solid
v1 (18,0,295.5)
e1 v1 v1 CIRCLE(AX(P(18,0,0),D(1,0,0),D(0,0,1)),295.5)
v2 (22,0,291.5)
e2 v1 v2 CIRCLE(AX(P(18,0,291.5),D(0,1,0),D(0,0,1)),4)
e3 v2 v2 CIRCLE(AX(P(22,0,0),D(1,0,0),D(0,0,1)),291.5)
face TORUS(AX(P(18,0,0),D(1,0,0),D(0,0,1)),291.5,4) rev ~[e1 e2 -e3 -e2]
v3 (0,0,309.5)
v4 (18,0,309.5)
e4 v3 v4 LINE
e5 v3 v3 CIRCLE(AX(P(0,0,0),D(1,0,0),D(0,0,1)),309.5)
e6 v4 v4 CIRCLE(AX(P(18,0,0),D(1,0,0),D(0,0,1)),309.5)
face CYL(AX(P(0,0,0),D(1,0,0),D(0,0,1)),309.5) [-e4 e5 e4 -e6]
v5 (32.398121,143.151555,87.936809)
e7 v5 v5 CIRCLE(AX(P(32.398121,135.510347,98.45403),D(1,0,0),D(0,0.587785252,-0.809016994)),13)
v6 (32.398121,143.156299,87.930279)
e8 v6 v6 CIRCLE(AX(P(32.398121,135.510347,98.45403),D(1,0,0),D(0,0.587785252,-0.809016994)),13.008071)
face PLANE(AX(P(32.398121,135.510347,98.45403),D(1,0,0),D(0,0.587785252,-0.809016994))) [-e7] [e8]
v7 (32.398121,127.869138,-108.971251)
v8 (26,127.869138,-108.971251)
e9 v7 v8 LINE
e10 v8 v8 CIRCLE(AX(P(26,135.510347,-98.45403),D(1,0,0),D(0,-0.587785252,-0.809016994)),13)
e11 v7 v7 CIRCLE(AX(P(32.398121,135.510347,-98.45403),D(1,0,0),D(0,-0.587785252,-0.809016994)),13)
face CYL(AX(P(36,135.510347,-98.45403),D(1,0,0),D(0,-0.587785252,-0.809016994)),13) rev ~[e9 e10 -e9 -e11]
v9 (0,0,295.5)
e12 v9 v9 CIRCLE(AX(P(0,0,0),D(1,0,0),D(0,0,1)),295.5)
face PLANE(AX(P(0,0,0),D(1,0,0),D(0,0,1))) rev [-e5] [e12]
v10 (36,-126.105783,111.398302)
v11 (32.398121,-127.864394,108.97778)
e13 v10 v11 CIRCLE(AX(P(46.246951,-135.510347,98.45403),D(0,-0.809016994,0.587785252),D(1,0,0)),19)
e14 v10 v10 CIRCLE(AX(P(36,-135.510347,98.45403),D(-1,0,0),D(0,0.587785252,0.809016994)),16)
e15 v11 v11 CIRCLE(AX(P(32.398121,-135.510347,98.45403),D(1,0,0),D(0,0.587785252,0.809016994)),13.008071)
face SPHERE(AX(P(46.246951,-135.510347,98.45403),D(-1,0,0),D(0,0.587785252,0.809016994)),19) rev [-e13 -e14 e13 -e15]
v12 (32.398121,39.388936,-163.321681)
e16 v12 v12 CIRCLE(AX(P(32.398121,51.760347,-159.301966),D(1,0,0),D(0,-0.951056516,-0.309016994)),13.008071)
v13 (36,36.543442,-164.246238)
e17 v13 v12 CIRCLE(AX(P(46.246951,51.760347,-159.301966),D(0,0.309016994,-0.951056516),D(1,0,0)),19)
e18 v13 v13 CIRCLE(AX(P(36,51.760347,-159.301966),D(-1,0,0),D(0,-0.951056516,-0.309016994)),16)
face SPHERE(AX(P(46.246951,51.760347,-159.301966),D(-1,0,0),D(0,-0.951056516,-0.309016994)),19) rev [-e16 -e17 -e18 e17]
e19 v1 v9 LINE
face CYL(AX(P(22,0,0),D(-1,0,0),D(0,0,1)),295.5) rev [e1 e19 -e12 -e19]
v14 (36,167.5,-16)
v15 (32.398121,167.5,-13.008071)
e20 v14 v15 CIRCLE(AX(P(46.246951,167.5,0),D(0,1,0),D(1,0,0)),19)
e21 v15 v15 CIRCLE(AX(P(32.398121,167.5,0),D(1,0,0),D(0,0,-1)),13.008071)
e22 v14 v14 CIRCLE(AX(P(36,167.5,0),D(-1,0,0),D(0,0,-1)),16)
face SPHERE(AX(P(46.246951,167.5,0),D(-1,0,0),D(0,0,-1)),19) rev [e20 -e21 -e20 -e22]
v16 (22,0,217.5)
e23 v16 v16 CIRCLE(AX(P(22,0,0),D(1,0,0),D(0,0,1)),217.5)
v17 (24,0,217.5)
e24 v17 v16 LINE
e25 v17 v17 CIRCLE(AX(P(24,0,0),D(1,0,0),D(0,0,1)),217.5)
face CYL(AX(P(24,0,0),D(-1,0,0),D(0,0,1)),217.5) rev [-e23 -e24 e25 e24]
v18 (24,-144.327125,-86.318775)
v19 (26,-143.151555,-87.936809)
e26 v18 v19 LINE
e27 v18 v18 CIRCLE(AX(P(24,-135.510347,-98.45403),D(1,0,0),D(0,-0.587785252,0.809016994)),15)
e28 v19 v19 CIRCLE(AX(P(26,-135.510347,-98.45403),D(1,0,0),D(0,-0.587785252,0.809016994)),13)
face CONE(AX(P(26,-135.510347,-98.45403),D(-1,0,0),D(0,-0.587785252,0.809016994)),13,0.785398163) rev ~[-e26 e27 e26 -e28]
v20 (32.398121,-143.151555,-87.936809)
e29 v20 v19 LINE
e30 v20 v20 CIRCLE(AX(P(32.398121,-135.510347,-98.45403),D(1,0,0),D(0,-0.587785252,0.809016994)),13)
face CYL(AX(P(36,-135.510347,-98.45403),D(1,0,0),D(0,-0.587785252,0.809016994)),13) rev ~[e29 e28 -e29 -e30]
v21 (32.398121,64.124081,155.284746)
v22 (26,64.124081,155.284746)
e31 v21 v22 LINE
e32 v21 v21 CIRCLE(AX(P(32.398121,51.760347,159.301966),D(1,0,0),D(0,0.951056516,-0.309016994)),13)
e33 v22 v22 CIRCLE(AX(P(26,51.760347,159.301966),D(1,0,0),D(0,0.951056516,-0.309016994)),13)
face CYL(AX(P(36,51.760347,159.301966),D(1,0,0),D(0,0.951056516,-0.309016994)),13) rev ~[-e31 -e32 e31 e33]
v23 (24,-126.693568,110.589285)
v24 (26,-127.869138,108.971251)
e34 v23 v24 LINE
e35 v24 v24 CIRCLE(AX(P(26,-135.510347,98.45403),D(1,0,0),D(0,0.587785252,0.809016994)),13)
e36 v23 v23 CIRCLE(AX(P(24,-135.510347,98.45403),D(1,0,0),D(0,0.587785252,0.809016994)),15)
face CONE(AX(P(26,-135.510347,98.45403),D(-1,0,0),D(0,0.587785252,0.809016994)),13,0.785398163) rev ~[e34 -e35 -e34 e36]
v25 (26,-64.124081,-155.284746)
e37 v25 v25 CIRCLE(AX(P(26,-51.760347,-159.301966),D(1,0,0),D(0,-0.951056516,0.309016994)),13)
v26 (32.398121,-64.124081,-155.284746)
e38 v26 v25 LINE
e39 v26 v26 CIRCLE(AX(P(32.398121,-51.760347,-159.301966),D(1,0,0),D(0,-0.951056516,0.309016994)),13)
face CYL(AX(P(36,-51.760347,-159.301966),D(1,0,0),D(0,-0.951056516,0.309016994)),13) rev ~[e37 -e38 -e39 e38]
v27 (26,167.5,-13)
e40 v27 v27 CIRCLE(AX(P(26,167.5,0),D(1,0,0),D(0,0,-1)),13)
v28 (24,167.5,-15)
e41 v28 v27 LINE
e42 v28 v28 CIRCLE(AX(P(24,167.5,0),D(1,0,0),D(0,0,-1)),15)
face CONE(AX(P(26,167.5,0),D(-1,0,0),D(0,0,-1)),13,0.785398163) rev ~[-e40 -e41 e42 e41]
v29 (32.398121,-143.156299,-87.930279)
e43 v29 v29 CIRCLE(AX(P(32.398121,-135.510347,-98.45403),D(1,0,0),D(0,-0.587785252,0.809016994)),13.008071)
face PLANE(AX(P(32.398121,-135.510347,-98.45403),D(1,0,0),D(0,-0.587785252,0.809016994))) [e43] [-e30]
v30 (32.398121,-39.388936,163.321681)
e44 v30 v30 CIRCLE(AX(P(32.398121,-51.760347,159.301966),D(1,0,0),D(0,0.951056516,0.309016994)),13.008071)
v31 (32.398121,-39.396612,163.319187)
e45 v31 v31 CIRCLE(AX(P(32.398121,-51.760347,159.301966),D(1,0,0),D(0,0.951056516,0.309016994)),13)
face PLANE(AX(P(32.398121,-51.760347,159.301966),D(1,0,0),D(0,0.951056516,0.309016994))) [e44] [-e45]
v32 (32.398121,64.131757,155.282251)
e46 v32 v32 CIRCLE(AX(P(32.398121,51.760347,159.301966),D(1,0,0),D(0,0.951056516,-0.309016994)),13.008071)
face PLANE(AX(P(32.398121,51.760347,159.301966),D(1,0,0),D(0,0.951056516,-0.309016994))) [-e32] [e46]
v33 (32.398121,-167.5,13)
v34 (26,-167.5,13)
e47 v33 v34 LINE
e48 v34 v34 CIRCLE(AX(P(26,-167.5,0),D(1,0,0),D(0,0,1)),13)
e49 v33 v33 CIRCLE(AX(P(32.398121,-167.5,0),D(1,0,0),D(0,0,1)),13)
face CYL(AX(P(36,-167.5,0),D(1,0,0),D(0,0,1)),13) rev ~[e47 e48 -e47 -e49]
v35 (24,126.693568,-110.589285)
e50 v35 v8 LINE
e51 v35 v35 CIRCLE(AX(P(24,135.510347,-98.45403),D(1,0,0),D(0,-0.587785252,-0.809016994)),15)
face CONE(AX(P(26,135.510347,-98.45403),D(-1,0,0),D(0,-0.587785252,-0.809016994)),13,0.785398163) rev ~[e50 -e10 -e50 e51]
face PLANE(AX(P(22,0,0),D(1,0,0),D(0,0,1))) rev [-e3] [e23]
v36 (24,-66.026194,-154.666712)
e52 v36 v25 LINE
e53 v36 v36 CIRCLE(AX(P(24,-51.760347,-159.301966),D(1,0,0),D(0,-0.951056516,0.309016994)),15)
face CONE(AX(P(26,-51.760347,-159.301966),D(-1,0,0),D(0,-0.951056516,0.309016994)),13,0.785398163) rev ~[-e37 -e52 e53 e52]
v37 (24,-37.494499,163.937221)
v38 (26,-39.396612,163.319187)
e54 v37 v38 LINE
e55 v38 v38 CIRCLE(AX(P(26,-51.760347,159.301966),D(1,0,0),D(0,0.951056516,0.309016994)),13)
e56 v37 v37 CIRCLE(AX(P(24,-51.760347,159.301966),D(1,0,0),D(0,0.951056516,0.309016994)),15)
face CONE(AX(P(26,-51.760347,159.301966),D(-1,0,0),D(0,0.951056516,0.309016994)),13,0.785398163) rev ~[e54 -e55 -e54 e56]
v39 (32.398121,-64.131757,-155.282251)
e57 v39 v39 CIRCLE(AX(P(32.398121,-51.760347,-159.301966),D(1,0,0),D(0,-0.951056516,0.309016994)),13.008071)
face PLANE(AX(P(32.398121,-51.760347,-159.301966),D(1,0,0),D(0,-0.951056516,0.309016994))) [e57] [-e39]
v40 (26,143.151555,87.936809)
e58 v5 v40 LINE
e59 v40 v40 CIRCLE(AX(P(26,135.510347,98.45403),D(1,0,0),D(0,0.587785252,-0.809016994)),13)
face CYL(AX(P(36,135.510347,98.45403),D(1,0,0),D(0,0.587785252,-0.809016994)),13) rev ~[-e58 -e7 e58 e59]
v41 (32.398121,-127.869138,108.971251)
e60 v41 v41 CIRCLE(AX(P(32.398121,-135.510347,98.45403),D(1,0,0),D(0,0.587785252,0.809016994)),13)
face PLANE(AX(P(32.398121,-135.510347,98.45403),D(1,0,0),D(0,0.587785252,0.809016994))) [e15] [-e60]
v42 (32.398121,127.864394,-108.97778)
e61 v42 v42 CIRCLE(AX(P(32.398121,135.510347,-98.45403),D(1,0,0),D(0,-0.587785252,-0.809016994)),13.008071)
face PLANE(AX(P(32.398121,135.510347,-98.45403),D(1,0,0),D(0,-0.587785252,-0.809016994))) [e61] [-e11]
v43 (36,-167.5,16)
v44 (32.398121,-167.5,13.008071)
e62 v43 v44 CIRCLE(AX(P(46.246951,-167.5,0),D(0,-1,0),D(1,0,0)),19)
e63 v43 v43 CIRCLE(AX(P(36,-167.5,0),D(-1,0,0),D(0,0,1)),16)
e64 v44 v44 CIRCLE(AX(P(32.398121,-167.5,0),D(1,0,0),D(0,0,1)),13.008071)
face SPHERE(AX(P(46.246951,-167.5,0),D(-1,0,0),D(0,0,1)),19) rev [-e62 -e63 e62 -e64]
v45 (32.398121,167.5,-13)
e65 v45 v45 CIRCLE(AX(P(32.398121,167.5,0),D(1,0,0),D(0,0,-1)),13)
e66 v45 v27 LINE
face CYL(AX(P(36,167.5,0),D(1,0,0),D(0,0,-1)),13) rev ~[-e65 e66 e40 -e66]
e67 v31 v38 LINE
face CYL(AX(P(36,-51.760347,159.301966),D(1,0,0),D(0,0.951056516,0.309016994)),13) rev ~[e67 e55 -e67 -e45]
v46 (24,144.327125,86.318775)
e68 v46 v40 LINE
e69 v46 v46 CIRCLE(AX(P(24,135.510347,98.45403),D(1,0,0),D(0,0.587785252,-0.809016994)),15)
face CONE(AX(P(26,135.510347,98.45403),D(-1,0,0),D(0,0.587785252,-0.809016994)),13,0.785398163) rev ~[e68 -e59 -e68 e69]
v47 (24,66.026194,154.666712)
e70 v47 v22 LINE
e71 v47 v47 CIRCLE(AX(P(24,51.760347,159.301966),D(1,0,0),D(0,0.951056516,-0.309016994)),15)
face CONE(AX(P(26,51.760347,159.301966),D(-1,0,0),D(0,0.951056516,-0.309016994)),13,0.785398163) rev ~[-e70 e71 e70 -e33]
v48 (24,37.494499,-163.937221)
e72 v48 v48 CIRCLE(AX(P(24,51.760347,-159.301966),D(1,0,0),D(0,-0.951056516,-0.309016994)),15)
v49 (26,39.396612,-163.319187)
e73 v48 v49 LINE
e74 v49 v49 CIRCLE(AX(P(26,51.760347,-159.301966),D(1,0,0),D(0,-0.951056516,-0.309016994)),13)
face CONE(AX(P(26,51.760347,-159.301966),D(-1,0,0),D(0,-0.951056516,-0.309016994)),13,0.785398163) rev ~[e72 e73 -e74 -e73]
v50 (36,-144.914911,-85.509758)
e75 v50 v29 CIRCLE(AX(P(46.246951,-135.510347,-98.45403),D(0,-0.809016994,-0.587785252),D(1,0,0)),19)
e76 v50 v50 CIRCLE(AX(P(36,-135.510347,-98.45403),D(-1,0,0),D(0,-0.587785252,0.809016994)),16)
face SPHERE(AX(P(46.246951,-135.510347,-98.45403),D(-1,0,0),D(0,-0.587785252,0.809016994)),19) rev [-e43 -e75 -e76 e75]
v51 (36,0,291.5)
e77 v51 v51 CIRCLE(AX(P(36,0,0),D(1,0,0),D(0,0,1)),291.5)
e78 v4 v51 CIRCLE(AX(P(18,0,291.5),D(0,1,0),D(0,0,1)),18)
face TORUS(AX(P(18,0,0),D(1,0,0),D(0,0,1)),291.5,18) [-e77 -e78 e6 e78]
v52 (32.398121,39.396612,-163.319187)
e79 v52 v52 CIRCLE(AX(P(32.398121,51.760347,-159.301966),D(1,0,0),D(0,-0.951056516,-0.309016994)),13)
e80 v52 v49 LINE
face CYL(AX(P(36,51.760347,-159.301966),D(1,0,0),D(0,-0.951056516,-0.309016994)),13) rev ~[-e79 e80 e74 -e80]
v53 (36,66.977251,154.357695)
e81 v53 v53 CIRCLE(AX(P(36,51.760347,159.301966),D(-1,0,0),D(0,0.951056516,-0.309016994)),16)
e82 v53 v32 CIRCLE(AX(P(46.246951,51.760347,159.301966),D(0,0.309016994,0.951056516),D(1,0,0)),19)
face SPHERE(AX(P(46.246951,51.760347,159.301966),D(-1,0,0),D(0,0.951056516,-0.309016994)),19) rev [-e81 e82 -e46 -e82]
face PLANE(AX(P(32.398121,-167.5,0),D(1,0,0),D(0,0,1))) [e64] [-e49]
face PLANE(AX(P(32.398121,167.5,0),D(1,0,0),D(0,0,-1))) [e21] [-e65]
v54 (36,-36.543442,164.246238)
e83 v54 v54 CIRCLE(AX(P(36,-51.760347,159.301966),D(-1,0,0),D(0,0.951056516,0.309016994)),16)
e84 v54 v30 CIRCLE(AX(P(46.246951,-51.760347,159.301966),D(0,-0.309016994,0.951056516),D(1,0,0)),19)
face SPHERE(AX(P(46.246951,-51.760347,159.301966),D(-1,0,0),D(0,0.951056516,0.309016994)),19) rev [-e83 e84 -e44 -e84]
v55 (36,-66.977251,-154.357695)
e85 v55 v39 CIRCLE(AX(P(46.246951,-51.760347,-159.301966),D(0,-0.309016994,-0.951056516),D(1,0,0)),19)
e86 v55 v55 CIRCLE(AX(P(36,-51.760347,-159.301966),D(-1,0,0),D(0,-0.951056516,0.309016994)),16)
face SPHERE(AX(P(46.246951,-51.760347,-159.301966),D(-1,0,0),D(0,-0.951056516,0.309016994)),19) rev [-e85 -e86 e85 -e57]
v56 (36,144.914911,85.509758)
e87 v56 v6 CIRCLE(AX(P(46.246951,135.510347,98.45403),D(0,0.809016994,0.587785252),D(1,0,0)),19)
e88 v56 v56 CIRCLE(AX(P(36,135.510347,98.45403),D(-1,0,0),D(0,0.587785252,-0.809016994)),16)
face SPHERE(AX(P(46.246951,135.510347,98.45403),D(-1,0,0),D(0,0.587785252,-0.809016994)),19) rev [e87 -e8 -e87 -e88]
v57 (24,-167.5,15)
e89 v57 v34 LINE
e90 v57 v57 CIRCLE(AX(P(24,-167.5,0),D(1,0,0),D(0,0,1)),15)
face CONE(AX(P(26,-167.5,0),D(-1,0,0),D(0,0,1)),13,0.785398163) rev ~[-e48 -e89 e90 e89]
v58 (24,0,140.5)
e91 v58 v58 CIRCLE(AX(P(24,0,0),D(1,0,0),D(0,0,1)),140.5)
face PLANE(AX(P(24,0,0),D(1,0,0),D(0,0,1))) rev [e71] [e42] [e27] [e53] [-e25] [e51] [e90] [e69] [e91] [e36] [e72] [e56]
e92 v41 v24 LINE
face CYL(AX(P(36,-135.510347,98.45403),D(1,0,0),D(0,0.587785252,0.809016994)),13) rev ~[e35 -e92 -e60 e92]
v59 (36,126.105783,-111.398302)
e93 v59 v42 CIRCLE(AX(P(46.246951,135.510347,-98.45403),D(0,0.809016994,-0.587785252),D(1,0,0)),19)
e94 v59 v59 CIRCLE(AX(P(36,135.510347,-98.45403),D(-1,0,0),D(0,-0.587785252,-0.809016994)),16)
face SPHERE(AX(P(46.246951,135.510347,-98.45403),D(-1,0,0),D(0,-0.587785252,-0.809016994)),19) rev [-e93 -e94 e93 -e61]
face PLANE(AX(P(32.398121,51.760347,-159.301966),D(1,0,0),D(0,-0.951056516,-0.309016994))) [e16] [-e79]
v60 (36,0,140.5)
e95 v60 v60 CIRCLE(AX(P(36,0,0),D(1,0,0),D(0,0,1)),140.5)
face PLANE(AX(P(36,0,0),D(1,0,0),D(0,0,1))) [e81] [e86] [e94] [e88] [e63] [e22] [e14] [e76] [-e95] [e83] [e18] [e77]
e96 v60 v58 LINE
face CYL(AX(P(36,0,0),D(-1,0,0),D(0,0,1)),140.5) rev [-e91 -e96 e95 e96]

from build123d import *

# Parameters (mm, degrees)
FILLET_1_R                           = 18
FILLET_2_R                           = 4
SKETCH_2_R                           = 13
CUT_EXTRUDE_1_DEPTH                  = 440.177071421
CHAMFER_1_SIZE                       = 2
PATTERN_CIRCULAR_1_COUNT             = 10
CHAMFER_1_OF_PATTERN_CIRCULAR_1_SIZE = 2


with BuildPart() as part:
    # 草图1 → 旋转1 (revolve)
    with BuildSketch(Plane.XY, mode=Mode.PRIVATE) as revolve_1_sk:
        Polygon((0, 309.5), (36, 309.5), (36, 140.5), (24, 140.5), (24, 217.5), (22, 217.5), (22, 295.5), (0, 295.5), align=None)
    revolve(revolve_1_sk.sketch.rotate(Axis((-295.4, 0, 0), (1, 0, 0)), 90), axis=Axis((-295.4, 0, 0), (1, 0, 0)))

    # 圆角1
    fillet_1_edges = [part.edges().sort_by_distance(p)[0] for p in [
        (36, 0, -309.5),
    ]]
    fillet(fillet_1_edges, radius=FILLET_1_R)

    # 圆角2
    fillet_2_edges = [part.edges().sort_by_distance(p)[0] for p in [
        (22, 0, -295.5),
    ]]
    fillet(fillet_2_edges, radius=FILLET_2_R)

    # 草图2 → 切除-拉伸1 (cut, through all)
    with BuildSketch(Plane(origin=(36, 0, 0), x_dir=(0, 0, -1), z_dir=(1, 0, 0))):
        with Locations((0, 167.5)):
            Circle(SKETCH_2_R)
    cut_extrude_1 = extrude(amount=-CUT_EXTRUDE_1_DEPTH, mode=Mode.SUBTRACT)

    # 倒角1
    chamfer_1_edges = [part.edges().sort_by_distance(p)[0] for p in [
        (24, 167.5, 13),
    ]]
    chamfer(chamfer_1_edges, length=CHAMFER_1_SIZE)

    # 草图3 → 切除-旋转1 (revolve, cut)
    with BuildSketch(Plane.XY, mode=Mode.PRIVATE) as cut_revolve_1_sk:
        with BuildLine():
            Line((32.398120874, 180.50807098), (32.398120874, 167.5))
            Line((32.398120874, 167.5), (65.246950766, 167.5))
            ThreePointArc((65.246950766, 167.5), (53.242386137, 185.165329999), (32.398120874, 180.50807098))
        make_face()
    cut_revolve_1 = revolve(cut_revolve_1_sk.sketch.rotate(Axis((0, 167.5, 0), (1, 0, 0)), 270), axis=Axis((0, 167.5, 0), (1, 0, 0)), mode=Mode.SUBTRACT)

    # 阵列(圆周)1: 切除-拉伸1, 切除-旋转1 ×10 about axis
    pattern_circular_1_axis = Axis((0, 0, 0), (1, 0, 0))
    add([cut_extrude_1.rotate(pattern_circular_1_axis, i * 360 / PATTERN_CIRCULAR_1_COUNT) for i in range(1, PATTERN_CIRCULAR_1_COUNT)], mode=Mode.SUBTRACT)
    add([cut_revolve_1.rotate(pattern_circular_1_axis, i * 360 / PATTERN_CIRCULAR_1_COUNT) for i in range(1, PATTERN_CIRCULAR_1_COUNT)], mode=Mode.SUBTRACT)

    # 倒角1 of 阵列(圆周)1
    chamfer_1_of_pattern_circular_1_edges = [part.edges().sort_by_distance(p)[0] for p in [
        (24, 127.869138278, 108.971250686),
        (24, 39.396611846, 163.319187406),
        (24, -64.12408127, 155.284745553),
        (24, -143.151554838, 87.936808832),
        (24, -167.5, -13),
        (24, -127.869138278, -108.971250686),
        (24, -39.396611846, -163.319187406),
        (24, 64.12408127, -155.284745553),
        (24, 143.151554838, -87.936808832),
    ]]
    chamfer(chamfer_1_of_pattern_circular_1_edges, length=CHAMFER_1_OF_PATTERN_CIRCULAR_1_SIZE)


solid = part.part
